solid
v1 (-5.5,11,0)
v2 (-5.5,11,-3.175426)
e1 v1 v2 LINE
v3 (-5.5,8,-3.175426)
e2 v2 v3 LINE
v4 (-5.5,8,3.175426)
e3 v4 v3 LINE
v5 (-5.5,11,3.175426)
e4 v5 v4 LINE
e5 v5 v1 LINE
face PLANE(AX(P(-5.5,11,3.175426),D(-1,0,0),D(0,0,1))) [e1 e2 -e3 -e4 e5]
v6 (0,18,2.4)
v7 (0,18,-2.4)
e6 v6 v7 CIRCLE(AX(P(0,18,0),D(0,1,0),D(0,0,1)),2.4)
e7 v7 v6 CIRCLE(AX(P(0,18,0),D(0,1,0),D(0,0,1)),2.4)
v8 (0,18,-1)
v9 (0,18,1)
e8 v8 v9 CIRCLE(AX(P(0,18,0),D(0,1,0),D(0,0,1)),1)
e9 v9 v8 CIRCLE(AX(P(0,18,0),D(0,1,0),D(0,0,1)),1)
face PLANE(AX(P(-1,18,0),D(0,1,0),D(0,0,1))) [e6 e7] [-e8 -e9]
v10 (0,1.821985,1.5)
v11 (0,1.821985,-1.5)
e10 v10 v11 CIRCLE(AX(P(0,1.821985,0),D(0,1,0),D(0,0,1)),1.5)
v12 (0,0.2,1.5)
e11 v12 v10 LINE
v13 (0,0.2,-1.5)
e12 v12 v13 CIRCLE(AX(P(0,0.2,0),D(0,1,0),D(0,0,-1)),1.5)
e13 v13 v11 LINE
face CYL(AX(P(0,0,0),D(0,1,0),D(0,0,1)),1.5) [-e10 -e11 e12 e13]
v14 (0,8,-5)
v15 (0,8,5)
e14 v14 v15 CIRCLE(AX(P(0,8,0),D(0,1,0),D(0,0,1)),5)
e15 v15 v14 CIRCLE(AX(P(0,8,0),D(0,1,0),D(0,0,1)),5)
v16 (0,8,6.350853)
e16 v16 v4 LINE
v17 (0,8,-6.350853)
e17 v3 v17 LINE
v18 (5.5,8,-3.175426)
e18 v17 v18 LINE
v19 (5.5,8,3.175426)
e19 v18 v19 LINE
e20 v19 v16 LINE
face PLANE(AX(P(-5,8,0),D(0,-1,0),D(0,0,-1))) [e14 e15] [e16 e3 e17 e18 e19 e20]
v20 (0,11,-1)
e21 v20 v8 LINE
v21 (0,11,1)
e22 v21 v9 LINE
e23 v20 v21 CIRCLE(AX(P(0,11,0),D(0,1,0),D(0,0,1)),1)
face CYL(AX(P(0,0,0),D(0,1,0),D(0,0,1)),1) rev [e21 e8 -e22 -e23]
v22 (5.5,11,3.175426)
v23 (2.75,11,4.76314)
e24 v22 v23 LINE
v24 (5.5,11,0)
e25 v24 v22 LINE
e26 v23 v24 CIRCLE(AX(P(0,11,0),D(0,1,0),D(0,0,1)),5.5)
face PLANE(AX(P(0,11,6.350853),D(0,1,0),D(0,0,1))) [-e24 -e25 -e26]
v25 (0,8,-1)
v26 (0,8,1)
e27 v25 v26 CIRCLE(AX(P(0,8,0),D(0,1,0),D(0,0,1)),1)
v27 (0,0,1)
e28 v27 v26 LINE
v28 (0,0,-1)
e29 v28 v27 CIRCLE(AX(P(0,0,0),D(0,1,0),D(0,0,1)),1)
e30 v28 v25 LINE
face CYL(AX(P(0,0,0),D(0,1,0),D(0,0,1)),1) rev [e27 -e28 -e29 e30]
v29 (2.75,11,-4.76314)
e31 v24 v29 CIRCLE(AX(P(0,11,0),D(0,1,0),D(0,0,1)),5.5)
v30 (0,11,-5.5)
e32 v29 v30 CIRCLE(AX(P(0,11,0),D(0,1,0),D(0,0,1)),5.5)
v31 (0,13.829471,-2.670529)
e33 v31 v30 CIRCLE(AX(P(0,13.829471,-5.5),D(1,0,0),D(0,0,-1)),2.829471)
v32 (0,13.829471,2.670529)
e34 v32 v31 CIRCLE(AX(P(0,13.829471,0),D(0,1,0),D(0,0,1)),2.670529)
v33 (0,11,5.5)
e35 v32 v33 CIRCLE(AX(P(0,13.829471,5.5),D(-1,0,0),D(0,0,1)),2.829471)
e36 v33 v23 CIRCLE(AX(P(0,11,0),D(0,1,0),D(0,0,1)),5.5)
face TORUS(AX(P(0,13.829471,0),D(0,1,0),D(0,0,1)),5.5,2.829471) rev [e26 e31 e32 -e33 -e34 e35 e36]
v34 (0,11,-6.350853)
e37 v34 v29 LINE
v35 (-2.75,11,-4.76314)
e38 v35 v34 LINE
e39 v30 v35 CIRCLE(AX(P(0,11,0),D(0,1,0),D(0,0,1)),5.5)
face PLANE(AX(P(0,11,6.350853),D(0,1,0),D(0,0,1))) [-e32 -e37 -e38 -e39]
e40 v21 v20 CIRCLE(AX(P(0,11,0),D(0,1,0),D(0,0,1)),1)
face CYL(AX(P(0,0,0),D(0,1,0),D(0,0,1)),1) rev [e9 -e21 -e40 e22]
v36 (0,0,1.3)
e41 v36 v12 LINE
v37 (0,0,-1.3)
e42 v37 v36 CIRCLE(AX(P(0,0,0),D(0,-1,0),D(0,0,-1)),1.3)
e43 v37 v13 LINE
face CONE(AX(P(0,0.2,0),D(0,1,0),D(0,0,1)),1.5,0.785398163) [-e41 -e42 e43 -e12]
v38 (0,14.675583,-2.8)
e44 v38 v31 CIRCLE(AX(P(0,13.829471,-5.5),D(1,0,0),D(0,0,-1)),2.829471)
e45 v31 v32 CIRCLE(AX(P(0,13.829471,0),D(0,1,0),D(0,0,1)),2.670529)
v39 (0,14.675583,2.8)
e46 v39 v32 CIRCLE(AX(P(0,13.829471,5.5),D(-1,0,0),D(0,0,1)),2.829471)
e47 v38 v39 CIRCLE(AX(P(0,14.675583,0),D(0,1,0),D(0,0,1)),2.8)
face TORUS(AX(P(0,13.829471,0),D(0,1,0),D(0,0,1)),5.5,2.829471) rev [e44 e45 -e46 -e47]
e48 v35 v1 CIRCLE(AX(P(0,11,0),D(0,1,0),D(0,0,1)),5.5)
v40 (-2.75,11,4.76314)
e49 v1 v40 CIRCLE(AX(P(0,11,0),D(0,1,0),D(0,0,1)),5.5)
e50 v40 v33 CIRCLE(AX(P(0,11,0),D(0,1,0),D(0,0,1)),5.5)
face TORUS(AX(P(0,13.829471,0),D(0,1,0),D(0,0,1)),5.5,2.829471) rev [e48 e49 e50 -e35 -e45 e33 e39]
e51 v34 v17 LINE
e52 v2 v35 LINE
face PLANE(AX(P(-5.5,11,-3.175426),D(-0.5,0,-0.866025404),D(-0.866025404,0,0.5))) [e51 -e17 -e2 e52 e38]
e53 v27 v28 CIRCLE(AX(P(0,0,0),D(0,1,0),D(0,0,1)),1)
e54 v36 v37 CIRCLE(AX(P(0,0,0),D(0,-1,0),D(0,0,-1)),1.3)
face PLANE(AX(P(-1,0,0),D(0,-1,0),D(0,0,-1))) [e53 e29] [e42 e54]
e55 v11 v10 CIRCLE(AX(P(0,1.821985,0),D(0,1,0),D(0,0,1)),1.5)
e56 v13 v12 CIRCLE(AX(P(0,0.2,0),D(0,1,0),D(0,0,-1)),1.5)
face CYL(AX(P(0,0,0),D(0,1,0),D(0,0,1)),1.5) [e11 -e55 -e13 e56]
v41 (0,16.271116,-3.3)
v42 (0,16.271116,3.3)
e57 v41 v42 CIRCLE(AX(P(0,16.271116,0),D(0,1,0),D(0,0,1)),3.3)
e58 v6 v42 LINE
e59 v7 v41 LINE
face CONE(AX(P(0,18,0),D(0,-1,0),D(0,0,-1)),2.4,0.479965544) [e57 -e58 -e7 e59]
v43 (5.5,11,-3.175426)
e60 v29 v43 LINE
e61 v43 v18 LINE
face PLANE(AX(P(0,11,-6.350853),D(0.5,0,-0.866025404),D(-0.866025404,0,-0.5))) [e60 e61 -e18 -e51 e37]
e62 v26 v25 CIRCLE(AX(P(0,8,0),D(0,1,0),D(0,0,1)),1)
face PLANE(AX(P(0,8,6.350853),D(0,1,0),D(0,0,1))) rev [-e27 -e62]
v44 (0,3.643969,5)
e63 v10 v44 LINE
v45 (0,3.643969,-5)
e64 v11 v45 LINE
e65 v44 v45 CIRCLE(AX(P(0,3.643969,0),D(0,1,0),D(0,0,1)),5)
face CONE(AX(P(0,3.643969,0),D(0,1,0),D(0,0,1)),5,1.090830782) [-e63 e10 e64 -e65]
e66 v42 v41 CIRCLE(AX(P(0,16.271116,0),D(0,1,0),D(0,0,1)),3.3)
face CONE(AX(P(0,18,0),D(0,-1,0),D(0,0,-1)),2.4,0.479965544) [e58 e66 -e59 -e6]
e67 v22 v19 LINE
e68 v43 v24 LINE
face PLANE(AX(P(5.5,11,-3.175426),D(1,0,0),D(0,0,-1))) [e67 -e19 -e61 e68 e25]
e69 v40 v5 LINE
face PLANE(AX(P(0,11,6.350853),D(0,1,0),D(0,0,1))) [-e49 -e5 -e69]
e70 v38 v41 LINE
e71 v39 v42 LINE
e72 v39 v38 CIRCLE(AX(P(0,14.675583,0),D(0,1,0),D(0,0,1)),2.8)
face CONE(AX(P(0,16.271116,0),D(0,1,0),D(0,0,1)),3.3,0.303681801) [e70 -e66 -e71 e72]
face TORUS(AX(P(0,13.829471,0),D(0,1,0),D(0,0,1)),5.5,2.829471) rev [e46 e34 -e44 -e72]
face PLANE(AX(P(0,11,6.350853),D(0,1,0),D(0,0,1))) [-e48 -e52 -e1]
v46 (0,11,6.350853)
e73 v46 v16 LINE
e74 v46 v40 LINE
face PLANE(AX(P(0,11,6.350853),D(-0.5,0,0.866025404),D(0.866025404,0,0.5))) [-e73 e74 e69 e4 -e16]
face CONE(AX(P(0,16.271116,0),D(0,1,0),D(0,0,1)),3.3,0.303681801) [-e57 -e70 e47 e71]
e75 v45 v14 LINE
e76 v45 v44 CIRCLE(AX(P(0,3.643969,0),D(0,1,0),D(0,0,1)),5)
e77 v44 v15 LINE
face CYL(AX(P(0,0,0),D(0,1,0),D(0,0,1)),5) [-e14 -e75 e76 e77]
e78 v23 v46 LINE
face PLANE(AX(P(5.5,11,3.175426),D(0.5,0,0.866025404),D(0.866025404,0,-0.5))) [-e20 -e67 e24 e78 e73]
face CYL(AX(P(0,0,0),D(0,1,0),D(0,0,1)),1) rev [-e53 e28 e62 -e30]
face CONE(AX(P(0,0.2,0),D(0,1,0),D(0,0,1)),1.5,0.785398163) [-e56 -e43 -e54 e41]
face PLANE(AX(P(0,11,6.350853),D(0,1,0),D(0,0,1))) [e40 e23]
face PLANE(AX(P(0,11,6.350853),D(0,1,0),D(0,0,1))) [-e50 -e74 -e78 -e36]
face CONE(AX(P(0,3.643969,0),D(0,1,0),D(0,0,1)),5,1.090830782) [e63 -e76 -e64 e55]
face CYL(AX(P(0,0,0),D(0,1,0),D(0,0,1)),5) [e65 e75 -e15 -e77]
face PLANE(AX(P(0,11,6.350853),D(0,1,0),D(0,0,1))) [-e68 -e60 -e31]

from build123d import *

# Parameters (mm, degrees)
EXTRUDE_1_DEPTH = 3
CHAMFER_1_SIZE  = 0.2


with BuildPart() as part:
    # 草图1 → 旋转2 (revolve)
    with BuildSketch(Plane.XY, mode=Mode.PRIVATE) as revolve_2_sk:
        with BuildLine():
            Line((-1, 18), (-2.4, 18))
            Line((-2.4, 18), (-3.3, 16.271116086))
            Line((-3.3, 16.271116086), (-2.8, 14.675583457))
            ThreePointArc((-2.8, 14.675583457), (-3.219653878, 12.154380629), (-5.5, 11))
            Line((-5.5, 11), (-5.5, 8))
            Line((-5.5, 8), (-5, 8))
            Line((-5, 8), (-5, 3.643969354))
            Line((-5, 3.643969354), (-1.5, 1.821984677))
            Line((-1.5, 1.821984677), (-1.5, 0))
            Line((-1.5, 0), (-1, 0))
            Line((-1, 0), (-1, 18))
        make_face()
    revolve(revolve_2_sk.sketch.rotate(Axis((0, 0, 0), (0, -1, 0)), 270), axis=Axis((0, 0, 0), (0, -1, 0)))

    # 草图2 → 拉伸1 (add)
    with BuildSketch(Plane.XZ.offset(-8)):
        Polygon((-5.5, 3.175426481), (-5.5, -3.175426481), (0, -6.350852961), (5.5, -3.175426481), (5.5, 3.175426481), (0, 6.350852961), align=None)
    extrude(amount=-EXTRUDE_1_DEPTH)

    # 倒角1
    chamfer_1_edges = [part.edges().sort_by_distance(p)[0] for p in [
        (0, 0, -1.5),
    ]]
    chamfer(chamfer_1_edges, length=CHAMFER_1_SIZE)


solid = part.part
